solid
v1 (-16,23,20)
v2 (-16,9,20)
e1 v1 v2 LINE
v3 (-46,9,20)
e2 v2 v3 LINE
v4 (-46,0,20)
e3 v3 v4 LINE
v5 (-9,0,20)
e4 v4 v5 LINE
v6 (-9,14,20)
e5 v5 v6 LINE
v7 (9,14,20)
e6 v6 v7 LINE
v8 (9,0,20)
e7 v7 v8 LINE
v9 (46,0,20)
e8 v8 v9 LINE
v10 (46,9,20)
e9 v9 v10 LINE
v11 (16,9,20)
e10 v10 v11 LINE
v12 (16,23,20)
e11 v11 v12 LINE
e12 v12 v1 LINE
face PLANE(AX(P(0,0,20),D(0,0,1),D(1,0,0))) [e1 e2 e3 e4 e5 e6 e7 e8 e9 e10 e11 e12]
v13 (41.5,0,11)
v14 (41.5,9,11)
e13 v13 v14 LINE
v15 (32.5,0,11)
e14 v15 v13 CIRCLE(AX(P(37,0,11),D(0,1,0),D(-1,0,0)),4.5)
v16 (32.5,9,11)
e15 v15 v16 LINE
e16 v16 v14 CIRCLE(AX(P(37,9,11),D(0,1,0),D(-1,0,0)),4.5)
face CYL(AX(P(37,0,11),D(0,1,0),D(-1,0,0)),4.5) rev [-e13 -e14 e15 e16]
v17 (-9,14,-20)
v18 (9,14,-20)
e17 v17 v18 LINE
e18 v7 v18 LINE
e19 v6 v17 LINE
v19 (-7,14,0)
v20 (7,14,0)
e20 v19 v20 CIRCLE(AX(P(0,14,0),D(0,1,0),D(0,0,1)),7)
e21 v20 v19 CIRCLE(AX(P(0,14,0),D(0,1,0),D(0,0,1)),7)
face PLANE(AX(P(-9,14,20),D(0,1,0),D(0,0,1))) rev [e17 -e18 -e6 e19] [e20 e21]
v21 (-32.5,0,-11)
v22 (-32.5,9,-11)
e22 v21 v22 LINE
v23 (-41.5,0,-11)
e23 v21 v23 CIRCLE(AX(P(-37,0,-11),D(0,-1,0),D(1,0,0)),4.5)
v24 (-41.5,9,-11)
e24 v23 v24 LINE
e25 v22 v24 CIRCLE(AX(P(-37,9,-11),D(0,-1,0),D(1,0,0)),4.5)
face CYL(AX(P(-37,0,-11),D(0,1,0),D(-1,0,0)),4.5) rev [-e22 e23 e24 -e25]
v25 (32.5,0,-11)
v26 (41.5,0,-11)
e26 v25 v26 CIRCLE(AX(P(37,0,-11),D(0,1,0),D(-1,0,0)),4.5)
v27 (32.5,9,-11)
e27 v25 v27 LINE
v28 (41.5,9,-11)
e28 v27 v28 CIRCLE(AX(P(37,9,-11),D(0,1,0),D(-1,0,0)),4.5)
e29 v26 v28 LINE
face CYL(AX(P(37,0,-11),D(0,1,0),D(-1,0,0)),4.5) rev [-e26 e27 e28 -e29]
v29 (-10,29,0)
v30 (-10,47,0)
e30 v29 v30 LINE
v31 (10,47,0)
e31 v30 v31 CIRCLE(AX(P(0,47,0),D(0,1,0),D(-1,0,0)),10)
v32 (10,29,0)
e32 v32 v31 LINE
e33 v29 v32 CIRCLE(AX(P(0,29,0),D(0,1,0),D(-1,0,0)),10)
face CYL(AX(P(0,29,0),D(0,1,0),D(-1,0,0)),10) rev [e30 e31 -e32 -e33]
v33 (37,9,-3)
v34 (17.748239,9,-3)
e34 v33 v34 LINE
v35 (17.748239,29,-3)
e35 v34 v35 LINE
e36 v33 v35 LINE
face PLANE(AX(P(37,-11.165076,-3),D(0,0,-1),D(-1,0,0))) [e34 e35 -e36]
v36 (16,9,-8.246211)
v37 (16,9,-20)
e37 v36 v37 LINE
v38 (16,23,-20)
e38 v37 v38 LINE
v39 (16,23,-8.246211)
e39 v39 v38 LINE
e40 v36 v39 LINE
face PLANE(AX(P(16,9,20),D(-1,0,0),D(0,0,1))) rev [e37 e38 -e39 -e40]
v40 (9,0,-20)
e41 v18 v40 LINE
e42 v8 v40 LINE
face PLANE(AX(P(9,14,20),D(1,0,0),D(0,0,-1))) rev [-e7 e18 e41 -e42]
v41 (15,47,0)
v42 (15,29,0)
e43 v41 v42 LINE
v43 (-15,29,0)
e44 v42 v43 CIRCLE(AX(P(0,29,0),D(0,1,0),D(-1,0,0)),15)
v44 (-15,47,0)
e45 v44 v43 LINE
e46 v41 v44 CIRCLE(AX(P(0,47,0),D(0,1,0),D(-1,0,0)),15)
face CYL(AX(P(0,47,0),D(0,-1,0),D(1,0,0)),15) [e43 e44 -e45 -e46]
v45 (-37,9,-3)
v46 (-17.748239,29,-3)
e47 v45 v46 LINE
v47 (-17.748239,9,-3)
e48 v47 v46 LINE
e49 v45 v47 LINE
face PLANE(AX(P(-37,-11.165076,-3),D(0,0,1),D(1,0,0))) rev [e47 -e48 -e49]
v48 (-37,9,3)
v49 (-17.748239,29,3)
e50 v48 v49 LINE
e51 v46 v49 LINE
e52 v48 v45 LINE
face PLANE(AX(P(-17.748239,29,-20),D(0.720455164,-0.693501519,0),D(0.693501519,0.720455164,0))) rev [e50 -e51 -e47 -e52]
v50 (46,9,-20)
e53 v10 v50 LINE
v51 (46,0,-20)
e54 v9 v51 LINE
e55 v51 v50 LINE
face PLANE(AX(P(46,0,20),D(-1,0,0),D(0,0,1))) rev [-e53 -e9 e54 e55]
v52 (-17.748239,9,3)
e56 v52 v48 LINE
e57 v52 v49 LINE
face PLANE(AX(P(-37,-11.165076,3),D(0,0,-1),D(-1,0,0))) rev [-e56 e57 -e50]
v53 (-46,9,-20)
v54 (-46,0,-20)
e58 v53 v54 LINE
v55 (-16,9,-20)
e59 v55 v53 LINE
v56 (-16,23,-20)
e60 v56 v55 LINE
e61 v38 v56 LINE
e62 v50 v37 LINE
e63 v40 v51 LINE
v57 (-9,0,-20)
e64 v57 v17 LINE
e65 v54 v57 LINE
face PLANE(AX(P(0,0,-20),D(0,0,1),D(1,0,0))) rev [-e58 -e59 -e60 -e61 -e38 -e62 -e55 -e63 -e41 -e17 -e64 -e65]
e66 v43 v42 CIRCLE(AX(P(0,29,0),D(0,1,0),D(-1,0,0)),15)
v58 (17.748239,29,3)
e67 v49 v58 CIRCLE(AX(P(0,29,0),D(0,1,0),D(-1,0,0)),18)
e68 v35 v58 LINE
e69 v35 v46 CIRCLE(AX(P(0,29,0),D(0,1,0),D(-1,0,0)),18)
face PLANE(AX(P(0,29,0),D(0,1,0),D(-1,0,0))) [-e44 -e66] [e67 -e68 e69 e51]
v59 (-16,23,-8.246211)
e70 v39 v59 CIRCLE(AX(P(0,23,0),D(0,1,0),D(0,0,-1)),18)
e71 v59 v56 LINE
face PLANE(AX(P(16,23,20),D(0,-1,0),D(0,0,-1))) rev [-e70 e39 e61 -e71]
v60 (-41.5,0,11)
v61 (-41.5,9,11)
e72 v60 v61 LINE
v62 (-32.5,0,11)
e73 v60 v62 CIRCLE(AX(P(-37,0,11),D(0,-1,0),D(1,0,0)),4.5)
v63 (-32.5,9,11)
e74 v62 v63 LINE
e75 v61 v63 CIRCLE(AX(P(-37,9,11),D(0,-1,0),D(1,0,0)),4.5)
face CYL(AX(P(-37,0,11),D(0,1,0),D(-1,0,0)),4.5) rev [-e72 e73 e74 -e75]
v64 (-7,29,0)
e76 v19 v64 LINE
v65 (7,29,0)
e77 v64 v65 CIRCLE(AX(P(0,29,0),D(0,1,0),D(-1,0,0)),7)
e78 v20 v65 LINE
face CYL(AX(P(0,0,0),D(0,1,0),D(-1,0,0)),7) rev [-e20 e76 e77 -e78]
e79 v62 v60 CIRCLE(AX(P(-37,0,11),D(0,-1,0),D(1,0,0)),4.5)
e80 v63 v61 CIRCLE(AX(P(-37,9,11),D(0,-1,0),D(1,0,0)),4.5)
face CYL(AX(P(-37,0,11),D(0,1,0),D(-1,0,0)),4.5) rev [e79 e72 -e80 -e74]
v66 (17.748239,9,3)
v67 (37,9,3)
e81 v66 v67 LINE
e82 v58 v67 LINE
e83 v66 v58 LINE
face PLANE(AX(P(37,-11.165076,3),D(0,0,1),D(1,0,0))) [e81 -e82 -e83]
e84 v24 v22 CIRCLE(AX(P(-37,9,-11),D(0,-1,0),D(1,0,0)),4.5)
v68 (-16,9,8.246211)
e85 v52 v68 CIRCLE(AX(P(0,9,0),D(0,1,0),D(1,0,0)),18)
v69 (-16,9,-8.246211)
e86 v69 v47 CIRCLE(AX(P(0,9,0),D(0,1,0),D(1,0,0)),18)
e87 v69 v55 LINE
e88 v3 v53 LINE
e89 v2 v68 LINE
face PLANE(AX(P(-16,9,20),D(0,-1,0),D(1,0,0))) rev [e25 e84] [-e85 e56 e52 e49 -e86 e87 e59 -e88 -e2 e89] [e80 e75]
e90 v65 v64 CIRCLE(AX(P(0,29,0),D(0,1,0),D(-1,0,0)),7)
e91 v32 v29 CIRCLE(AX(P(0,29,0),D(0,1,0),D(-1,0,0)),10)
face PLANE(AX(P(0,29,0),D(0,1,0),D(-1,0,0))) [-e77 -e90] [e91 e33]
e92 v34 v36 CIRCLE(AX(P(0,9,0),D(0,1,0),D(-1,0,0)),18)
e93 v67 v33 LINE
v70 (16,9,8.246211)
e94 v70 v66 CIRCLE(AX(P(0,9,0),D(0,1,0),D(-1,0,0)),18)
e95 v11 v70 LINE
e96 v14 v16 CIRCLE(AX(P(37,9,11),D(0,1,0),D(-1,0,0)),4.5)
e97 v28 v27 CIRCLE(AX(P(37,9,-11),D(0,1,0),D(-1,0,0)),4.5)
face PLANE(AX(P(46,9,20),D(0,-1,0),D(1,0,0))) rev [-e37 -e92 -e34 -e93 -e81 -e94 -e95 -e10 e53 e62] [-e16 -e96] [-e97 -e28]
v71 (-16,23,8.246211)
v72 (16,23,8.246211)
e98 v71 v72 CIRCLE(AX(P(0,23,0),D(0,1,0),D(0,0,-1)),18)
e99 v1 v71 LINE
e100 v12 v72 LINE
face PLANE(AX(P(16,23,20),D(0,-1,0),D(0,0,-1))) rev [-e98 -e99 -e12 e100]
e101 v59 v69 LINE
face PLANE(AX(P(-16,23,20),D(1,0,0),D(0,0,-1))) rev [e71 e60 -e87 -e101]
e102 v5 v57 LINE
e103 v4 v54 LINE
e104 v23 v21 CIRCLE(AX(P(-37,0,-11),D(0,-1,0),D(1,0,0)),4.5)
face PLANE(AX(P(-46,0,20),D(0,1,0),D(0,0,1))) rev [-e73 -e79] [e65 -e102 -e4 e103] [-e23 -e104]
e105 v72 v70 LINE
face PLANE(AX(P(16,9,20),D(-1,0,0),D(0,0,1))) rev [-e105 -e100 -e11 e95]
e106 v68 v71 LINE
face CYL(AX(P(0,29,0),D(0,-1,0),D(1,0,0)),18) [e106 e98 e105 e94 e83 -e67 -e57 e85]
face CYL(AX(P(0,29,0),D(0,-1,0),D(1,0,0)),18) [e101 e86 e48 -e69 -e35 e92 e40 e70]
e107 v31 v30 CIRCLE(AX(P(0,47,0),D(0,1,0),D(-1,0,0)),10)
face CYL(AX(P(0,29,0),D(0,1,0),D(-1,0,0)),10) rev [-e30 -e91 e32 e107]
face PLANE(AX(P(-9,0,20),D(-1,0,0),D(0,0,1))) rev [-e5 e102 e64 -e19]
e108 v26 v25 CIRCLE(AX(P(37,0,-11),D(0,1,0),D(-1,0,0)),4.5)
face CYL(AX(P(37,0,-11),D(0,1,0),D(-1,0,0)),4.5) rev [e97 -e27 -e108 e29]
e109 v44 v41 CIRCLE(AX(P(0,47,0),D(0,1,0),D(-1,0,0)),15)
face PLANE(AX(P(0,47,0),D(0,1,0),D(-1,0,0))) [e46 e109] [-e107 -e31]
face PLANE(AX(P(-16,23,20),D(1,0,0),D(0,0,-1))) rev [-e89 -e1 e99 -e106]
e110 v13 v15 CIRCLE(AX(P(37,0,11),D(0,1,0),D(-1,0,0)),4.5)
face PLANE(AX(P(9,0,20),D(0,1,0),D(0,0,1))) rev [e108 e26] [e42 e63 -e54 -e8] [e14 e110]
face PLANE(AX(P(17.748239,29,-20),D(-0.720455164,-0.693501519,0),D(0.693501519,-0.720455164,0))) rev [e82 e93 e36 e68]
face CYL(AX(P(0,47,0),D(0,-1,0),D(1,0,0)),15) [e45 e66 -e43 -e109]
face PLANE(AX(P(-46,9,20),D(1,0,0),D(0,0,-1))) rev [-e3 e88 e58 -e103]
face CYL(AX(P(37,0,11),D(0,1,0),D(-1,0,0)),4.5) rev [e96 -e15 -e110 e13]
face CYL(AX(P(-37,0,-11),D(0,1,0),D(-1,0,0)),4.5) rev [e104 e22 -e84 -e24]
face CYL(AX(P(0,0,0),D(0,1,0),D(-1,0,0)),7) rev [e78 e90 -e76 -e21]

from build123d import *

# Parameters (mm, degrees)
STEPPED_BASE_DEPTH          = 20
COLLAR_36_SKETCH_R          = 18
COLLAR_36_DEPTH             = 20
COLLAR_TRIM_SKETCH_W        = 18
COLLAR_TRIM_SKETCH_H        = 5
COLLAR_TRIM_CUT_DEPTH       = 68.505555327
HUB_30_SKETCH_R             = 15
HUB_30_DEPTH                = 18
COUNTERBORE_20_SKETCH_R     = 10
COUNTERBORE_20_DEPTH        = 18
BORE_14_SKETCH_R            = 7
BORE_14_DEPTH               = 58.939623747
MOUNTING_HOLE_9_SKETCH_R    = 4.5
MOUNTING_HOLES_9_DEPTH      = 63.92853089
SUPPORT_START               = -20
SUPPORT_RIB_DEPTH           = 20
RIB_TRIM_CUT_DEPTH          = 70.670653793
MIRRORED_RIB_TRIM_CUT_DEPTH = 70.670653793


with BuildPart() as part:
    # Base Profile Sketch → Stepped Base (new, symmetric)
    with BuildSketch(Plane.XY):
        Polygon((-46, 0), (-9, 0), (-9, 14), (9, 14), (9, 0), (46, 0), (46, 9), (16, 9), (16, 23), (-16, 23), (-16, 9), (-46, 9), align=None)
    extrude(amount=STEPPED_BASE_DEPTH, both=True)

    # Collar Ø36 Sketch → Collar Ø36 (add)
    with BuildSketch(Plane(origin=(0, 9, 0), x_dir=(1, 0, 0), z_dir=(0, 1, 0))):
        with Locations(Location((0, 0, 0), (0, 0, 27.266044451))):
            Circle(COLLAR_36_SKETCH_R)
    extrude(amount=COLLAR_36_DEPTH)

    # Collar Trim Sketch → Collar Trim Cut (cut, through all)
    with BuildSketch(Plane.XY.offset(20)):
        with Locations((0, 11.5)):
            Rectangle(COLLAR_TRIM_SKETCH_W, COLLAR_TRIM_SKETCH_H)
    extrude(amount=-COLLAR_TRIM_CUT_DEPTH, mode=Mode.SUBTRACT)

    # Hub Ø30 Sketch → Hub Ø30 (add)
    with BuildSketch(Plane(origin=(0, 29, 0), x_dir=(1, 0, 0), z_dir=(0, 1, 0))):
        with Locations(Location((0, 0, 0), (0, 0, 180))):
            Circle(HUB_30_SKETCH_R)
    extrude(amount=HUB_30_DEPTH)

    # Counterbore Ø20 Sketch → Counterbore Ø20 (cut)
    with BuildSketch(Plane(origin=(0, 47, 0), x_dir=(1, 0, 0), z_dir=(0, 1, 0))):
        with Locations(Location((0, 0, 0), (0, 0, 180))):
            Circle(COUNTERBORE_20_SKETCH_R)
    extrude(amount=-COUNTERBORE_20_DEPTH, mode=Mode.SUBTRACT)

    # Bore Ø14 Sketch → Bore Ø14 (cut, through all)
    with BuildSketch(Plane(origin=(0, 29, 0), x_dir=(1, 0, 0), z_dir=(0, 1, 0))):
        with Locations(Location((0, 0, 0), (0, 0, 180))):
            Circle(BORE_14_SKETCH_R)
    extrude(amount=-BORE_14_DEPTH, mode=Mode.SUBTRACT)

    # Mounting Hole Ø9 Sketch → Mounting Holes Ø9 (cut, through all)
    with BuildSketch(Plane(origin=(0, 9, 0), x_dir=(1, 0, 0), z_dir=(0, 1, 0))):
        with Locations(Location((37, -11, 0), (0, 0, 180))):
            Circle(MOUNTING_HOLE_9_SKETCH_R)
        with Locations(Location((37, 11, 0), (0, 0, 180))):
            Circle(MOUNTING_HOLE_9_SKETCH_R)
    mounting_holes_9 = extrude(amount=-MOUNTING_HOLES_9_DEPTH, mode=Mode.SUBTRACT)

    # Support Rib Sketch → Support Rib (add)
    with BuildSketch(Plane(origin=(0, 29, 0), x_dir=(1, 0, 0), z_dir=(0, 1, 0)).offset(SUPPORT_START)):
        with BuildLine():
            Line((37, 3), (37, -3))
            Line((37, -3), (17.748239349, -3))
            ThreePointArc((17.748239349, -3), (18, 0), (17.748239349, 3))
            Line((17.748239349, 3), (37, 3))
        make_face()
    support_rib = extrude(amount=SUPPORT_RIB_DEPTH)

    # Rib Trim Sketch → Rib Trim Cut (cut, through all)
    with BuildSketch(Plane.XY.offset(3)):
        Polygon((17.748239349, 29), (37, 9), (37, 29), align=None)
    extrude(amount=-RIB_TRIM_CUT_DEPTH, mode=Mode.SUBTRACT)

    # Rib and Holes Mirror: Mounting Holes Ø9, Support Rib across plane
    add(mounting_holes_9.mirror(Plane(origin=(0, 0, 0), x_dir=(0, 0, 1), z_dir=(1, 0, 0))), mode=Mode.SUBTRACT)
    add(support_rib.mirror(Plane(origin=(0, 0, 0), x_dir=(0, 0, 1), z_dir=(1, 0, 0))))

    # Mirrored Rib Trim Sketch → Mirrored Rib Trim Cut (cut, through all)
    with BuildSketch(Plane.XY.offset(3)):
        Polygon((-17.748239349, 29), (-37, 9), (-37, 29), align=None)
    extrude(amount=-MIRRORED_RIB_TRIM_CUT_DEPTH, mode=Mode.SUBTRACT)


solid = part.part
